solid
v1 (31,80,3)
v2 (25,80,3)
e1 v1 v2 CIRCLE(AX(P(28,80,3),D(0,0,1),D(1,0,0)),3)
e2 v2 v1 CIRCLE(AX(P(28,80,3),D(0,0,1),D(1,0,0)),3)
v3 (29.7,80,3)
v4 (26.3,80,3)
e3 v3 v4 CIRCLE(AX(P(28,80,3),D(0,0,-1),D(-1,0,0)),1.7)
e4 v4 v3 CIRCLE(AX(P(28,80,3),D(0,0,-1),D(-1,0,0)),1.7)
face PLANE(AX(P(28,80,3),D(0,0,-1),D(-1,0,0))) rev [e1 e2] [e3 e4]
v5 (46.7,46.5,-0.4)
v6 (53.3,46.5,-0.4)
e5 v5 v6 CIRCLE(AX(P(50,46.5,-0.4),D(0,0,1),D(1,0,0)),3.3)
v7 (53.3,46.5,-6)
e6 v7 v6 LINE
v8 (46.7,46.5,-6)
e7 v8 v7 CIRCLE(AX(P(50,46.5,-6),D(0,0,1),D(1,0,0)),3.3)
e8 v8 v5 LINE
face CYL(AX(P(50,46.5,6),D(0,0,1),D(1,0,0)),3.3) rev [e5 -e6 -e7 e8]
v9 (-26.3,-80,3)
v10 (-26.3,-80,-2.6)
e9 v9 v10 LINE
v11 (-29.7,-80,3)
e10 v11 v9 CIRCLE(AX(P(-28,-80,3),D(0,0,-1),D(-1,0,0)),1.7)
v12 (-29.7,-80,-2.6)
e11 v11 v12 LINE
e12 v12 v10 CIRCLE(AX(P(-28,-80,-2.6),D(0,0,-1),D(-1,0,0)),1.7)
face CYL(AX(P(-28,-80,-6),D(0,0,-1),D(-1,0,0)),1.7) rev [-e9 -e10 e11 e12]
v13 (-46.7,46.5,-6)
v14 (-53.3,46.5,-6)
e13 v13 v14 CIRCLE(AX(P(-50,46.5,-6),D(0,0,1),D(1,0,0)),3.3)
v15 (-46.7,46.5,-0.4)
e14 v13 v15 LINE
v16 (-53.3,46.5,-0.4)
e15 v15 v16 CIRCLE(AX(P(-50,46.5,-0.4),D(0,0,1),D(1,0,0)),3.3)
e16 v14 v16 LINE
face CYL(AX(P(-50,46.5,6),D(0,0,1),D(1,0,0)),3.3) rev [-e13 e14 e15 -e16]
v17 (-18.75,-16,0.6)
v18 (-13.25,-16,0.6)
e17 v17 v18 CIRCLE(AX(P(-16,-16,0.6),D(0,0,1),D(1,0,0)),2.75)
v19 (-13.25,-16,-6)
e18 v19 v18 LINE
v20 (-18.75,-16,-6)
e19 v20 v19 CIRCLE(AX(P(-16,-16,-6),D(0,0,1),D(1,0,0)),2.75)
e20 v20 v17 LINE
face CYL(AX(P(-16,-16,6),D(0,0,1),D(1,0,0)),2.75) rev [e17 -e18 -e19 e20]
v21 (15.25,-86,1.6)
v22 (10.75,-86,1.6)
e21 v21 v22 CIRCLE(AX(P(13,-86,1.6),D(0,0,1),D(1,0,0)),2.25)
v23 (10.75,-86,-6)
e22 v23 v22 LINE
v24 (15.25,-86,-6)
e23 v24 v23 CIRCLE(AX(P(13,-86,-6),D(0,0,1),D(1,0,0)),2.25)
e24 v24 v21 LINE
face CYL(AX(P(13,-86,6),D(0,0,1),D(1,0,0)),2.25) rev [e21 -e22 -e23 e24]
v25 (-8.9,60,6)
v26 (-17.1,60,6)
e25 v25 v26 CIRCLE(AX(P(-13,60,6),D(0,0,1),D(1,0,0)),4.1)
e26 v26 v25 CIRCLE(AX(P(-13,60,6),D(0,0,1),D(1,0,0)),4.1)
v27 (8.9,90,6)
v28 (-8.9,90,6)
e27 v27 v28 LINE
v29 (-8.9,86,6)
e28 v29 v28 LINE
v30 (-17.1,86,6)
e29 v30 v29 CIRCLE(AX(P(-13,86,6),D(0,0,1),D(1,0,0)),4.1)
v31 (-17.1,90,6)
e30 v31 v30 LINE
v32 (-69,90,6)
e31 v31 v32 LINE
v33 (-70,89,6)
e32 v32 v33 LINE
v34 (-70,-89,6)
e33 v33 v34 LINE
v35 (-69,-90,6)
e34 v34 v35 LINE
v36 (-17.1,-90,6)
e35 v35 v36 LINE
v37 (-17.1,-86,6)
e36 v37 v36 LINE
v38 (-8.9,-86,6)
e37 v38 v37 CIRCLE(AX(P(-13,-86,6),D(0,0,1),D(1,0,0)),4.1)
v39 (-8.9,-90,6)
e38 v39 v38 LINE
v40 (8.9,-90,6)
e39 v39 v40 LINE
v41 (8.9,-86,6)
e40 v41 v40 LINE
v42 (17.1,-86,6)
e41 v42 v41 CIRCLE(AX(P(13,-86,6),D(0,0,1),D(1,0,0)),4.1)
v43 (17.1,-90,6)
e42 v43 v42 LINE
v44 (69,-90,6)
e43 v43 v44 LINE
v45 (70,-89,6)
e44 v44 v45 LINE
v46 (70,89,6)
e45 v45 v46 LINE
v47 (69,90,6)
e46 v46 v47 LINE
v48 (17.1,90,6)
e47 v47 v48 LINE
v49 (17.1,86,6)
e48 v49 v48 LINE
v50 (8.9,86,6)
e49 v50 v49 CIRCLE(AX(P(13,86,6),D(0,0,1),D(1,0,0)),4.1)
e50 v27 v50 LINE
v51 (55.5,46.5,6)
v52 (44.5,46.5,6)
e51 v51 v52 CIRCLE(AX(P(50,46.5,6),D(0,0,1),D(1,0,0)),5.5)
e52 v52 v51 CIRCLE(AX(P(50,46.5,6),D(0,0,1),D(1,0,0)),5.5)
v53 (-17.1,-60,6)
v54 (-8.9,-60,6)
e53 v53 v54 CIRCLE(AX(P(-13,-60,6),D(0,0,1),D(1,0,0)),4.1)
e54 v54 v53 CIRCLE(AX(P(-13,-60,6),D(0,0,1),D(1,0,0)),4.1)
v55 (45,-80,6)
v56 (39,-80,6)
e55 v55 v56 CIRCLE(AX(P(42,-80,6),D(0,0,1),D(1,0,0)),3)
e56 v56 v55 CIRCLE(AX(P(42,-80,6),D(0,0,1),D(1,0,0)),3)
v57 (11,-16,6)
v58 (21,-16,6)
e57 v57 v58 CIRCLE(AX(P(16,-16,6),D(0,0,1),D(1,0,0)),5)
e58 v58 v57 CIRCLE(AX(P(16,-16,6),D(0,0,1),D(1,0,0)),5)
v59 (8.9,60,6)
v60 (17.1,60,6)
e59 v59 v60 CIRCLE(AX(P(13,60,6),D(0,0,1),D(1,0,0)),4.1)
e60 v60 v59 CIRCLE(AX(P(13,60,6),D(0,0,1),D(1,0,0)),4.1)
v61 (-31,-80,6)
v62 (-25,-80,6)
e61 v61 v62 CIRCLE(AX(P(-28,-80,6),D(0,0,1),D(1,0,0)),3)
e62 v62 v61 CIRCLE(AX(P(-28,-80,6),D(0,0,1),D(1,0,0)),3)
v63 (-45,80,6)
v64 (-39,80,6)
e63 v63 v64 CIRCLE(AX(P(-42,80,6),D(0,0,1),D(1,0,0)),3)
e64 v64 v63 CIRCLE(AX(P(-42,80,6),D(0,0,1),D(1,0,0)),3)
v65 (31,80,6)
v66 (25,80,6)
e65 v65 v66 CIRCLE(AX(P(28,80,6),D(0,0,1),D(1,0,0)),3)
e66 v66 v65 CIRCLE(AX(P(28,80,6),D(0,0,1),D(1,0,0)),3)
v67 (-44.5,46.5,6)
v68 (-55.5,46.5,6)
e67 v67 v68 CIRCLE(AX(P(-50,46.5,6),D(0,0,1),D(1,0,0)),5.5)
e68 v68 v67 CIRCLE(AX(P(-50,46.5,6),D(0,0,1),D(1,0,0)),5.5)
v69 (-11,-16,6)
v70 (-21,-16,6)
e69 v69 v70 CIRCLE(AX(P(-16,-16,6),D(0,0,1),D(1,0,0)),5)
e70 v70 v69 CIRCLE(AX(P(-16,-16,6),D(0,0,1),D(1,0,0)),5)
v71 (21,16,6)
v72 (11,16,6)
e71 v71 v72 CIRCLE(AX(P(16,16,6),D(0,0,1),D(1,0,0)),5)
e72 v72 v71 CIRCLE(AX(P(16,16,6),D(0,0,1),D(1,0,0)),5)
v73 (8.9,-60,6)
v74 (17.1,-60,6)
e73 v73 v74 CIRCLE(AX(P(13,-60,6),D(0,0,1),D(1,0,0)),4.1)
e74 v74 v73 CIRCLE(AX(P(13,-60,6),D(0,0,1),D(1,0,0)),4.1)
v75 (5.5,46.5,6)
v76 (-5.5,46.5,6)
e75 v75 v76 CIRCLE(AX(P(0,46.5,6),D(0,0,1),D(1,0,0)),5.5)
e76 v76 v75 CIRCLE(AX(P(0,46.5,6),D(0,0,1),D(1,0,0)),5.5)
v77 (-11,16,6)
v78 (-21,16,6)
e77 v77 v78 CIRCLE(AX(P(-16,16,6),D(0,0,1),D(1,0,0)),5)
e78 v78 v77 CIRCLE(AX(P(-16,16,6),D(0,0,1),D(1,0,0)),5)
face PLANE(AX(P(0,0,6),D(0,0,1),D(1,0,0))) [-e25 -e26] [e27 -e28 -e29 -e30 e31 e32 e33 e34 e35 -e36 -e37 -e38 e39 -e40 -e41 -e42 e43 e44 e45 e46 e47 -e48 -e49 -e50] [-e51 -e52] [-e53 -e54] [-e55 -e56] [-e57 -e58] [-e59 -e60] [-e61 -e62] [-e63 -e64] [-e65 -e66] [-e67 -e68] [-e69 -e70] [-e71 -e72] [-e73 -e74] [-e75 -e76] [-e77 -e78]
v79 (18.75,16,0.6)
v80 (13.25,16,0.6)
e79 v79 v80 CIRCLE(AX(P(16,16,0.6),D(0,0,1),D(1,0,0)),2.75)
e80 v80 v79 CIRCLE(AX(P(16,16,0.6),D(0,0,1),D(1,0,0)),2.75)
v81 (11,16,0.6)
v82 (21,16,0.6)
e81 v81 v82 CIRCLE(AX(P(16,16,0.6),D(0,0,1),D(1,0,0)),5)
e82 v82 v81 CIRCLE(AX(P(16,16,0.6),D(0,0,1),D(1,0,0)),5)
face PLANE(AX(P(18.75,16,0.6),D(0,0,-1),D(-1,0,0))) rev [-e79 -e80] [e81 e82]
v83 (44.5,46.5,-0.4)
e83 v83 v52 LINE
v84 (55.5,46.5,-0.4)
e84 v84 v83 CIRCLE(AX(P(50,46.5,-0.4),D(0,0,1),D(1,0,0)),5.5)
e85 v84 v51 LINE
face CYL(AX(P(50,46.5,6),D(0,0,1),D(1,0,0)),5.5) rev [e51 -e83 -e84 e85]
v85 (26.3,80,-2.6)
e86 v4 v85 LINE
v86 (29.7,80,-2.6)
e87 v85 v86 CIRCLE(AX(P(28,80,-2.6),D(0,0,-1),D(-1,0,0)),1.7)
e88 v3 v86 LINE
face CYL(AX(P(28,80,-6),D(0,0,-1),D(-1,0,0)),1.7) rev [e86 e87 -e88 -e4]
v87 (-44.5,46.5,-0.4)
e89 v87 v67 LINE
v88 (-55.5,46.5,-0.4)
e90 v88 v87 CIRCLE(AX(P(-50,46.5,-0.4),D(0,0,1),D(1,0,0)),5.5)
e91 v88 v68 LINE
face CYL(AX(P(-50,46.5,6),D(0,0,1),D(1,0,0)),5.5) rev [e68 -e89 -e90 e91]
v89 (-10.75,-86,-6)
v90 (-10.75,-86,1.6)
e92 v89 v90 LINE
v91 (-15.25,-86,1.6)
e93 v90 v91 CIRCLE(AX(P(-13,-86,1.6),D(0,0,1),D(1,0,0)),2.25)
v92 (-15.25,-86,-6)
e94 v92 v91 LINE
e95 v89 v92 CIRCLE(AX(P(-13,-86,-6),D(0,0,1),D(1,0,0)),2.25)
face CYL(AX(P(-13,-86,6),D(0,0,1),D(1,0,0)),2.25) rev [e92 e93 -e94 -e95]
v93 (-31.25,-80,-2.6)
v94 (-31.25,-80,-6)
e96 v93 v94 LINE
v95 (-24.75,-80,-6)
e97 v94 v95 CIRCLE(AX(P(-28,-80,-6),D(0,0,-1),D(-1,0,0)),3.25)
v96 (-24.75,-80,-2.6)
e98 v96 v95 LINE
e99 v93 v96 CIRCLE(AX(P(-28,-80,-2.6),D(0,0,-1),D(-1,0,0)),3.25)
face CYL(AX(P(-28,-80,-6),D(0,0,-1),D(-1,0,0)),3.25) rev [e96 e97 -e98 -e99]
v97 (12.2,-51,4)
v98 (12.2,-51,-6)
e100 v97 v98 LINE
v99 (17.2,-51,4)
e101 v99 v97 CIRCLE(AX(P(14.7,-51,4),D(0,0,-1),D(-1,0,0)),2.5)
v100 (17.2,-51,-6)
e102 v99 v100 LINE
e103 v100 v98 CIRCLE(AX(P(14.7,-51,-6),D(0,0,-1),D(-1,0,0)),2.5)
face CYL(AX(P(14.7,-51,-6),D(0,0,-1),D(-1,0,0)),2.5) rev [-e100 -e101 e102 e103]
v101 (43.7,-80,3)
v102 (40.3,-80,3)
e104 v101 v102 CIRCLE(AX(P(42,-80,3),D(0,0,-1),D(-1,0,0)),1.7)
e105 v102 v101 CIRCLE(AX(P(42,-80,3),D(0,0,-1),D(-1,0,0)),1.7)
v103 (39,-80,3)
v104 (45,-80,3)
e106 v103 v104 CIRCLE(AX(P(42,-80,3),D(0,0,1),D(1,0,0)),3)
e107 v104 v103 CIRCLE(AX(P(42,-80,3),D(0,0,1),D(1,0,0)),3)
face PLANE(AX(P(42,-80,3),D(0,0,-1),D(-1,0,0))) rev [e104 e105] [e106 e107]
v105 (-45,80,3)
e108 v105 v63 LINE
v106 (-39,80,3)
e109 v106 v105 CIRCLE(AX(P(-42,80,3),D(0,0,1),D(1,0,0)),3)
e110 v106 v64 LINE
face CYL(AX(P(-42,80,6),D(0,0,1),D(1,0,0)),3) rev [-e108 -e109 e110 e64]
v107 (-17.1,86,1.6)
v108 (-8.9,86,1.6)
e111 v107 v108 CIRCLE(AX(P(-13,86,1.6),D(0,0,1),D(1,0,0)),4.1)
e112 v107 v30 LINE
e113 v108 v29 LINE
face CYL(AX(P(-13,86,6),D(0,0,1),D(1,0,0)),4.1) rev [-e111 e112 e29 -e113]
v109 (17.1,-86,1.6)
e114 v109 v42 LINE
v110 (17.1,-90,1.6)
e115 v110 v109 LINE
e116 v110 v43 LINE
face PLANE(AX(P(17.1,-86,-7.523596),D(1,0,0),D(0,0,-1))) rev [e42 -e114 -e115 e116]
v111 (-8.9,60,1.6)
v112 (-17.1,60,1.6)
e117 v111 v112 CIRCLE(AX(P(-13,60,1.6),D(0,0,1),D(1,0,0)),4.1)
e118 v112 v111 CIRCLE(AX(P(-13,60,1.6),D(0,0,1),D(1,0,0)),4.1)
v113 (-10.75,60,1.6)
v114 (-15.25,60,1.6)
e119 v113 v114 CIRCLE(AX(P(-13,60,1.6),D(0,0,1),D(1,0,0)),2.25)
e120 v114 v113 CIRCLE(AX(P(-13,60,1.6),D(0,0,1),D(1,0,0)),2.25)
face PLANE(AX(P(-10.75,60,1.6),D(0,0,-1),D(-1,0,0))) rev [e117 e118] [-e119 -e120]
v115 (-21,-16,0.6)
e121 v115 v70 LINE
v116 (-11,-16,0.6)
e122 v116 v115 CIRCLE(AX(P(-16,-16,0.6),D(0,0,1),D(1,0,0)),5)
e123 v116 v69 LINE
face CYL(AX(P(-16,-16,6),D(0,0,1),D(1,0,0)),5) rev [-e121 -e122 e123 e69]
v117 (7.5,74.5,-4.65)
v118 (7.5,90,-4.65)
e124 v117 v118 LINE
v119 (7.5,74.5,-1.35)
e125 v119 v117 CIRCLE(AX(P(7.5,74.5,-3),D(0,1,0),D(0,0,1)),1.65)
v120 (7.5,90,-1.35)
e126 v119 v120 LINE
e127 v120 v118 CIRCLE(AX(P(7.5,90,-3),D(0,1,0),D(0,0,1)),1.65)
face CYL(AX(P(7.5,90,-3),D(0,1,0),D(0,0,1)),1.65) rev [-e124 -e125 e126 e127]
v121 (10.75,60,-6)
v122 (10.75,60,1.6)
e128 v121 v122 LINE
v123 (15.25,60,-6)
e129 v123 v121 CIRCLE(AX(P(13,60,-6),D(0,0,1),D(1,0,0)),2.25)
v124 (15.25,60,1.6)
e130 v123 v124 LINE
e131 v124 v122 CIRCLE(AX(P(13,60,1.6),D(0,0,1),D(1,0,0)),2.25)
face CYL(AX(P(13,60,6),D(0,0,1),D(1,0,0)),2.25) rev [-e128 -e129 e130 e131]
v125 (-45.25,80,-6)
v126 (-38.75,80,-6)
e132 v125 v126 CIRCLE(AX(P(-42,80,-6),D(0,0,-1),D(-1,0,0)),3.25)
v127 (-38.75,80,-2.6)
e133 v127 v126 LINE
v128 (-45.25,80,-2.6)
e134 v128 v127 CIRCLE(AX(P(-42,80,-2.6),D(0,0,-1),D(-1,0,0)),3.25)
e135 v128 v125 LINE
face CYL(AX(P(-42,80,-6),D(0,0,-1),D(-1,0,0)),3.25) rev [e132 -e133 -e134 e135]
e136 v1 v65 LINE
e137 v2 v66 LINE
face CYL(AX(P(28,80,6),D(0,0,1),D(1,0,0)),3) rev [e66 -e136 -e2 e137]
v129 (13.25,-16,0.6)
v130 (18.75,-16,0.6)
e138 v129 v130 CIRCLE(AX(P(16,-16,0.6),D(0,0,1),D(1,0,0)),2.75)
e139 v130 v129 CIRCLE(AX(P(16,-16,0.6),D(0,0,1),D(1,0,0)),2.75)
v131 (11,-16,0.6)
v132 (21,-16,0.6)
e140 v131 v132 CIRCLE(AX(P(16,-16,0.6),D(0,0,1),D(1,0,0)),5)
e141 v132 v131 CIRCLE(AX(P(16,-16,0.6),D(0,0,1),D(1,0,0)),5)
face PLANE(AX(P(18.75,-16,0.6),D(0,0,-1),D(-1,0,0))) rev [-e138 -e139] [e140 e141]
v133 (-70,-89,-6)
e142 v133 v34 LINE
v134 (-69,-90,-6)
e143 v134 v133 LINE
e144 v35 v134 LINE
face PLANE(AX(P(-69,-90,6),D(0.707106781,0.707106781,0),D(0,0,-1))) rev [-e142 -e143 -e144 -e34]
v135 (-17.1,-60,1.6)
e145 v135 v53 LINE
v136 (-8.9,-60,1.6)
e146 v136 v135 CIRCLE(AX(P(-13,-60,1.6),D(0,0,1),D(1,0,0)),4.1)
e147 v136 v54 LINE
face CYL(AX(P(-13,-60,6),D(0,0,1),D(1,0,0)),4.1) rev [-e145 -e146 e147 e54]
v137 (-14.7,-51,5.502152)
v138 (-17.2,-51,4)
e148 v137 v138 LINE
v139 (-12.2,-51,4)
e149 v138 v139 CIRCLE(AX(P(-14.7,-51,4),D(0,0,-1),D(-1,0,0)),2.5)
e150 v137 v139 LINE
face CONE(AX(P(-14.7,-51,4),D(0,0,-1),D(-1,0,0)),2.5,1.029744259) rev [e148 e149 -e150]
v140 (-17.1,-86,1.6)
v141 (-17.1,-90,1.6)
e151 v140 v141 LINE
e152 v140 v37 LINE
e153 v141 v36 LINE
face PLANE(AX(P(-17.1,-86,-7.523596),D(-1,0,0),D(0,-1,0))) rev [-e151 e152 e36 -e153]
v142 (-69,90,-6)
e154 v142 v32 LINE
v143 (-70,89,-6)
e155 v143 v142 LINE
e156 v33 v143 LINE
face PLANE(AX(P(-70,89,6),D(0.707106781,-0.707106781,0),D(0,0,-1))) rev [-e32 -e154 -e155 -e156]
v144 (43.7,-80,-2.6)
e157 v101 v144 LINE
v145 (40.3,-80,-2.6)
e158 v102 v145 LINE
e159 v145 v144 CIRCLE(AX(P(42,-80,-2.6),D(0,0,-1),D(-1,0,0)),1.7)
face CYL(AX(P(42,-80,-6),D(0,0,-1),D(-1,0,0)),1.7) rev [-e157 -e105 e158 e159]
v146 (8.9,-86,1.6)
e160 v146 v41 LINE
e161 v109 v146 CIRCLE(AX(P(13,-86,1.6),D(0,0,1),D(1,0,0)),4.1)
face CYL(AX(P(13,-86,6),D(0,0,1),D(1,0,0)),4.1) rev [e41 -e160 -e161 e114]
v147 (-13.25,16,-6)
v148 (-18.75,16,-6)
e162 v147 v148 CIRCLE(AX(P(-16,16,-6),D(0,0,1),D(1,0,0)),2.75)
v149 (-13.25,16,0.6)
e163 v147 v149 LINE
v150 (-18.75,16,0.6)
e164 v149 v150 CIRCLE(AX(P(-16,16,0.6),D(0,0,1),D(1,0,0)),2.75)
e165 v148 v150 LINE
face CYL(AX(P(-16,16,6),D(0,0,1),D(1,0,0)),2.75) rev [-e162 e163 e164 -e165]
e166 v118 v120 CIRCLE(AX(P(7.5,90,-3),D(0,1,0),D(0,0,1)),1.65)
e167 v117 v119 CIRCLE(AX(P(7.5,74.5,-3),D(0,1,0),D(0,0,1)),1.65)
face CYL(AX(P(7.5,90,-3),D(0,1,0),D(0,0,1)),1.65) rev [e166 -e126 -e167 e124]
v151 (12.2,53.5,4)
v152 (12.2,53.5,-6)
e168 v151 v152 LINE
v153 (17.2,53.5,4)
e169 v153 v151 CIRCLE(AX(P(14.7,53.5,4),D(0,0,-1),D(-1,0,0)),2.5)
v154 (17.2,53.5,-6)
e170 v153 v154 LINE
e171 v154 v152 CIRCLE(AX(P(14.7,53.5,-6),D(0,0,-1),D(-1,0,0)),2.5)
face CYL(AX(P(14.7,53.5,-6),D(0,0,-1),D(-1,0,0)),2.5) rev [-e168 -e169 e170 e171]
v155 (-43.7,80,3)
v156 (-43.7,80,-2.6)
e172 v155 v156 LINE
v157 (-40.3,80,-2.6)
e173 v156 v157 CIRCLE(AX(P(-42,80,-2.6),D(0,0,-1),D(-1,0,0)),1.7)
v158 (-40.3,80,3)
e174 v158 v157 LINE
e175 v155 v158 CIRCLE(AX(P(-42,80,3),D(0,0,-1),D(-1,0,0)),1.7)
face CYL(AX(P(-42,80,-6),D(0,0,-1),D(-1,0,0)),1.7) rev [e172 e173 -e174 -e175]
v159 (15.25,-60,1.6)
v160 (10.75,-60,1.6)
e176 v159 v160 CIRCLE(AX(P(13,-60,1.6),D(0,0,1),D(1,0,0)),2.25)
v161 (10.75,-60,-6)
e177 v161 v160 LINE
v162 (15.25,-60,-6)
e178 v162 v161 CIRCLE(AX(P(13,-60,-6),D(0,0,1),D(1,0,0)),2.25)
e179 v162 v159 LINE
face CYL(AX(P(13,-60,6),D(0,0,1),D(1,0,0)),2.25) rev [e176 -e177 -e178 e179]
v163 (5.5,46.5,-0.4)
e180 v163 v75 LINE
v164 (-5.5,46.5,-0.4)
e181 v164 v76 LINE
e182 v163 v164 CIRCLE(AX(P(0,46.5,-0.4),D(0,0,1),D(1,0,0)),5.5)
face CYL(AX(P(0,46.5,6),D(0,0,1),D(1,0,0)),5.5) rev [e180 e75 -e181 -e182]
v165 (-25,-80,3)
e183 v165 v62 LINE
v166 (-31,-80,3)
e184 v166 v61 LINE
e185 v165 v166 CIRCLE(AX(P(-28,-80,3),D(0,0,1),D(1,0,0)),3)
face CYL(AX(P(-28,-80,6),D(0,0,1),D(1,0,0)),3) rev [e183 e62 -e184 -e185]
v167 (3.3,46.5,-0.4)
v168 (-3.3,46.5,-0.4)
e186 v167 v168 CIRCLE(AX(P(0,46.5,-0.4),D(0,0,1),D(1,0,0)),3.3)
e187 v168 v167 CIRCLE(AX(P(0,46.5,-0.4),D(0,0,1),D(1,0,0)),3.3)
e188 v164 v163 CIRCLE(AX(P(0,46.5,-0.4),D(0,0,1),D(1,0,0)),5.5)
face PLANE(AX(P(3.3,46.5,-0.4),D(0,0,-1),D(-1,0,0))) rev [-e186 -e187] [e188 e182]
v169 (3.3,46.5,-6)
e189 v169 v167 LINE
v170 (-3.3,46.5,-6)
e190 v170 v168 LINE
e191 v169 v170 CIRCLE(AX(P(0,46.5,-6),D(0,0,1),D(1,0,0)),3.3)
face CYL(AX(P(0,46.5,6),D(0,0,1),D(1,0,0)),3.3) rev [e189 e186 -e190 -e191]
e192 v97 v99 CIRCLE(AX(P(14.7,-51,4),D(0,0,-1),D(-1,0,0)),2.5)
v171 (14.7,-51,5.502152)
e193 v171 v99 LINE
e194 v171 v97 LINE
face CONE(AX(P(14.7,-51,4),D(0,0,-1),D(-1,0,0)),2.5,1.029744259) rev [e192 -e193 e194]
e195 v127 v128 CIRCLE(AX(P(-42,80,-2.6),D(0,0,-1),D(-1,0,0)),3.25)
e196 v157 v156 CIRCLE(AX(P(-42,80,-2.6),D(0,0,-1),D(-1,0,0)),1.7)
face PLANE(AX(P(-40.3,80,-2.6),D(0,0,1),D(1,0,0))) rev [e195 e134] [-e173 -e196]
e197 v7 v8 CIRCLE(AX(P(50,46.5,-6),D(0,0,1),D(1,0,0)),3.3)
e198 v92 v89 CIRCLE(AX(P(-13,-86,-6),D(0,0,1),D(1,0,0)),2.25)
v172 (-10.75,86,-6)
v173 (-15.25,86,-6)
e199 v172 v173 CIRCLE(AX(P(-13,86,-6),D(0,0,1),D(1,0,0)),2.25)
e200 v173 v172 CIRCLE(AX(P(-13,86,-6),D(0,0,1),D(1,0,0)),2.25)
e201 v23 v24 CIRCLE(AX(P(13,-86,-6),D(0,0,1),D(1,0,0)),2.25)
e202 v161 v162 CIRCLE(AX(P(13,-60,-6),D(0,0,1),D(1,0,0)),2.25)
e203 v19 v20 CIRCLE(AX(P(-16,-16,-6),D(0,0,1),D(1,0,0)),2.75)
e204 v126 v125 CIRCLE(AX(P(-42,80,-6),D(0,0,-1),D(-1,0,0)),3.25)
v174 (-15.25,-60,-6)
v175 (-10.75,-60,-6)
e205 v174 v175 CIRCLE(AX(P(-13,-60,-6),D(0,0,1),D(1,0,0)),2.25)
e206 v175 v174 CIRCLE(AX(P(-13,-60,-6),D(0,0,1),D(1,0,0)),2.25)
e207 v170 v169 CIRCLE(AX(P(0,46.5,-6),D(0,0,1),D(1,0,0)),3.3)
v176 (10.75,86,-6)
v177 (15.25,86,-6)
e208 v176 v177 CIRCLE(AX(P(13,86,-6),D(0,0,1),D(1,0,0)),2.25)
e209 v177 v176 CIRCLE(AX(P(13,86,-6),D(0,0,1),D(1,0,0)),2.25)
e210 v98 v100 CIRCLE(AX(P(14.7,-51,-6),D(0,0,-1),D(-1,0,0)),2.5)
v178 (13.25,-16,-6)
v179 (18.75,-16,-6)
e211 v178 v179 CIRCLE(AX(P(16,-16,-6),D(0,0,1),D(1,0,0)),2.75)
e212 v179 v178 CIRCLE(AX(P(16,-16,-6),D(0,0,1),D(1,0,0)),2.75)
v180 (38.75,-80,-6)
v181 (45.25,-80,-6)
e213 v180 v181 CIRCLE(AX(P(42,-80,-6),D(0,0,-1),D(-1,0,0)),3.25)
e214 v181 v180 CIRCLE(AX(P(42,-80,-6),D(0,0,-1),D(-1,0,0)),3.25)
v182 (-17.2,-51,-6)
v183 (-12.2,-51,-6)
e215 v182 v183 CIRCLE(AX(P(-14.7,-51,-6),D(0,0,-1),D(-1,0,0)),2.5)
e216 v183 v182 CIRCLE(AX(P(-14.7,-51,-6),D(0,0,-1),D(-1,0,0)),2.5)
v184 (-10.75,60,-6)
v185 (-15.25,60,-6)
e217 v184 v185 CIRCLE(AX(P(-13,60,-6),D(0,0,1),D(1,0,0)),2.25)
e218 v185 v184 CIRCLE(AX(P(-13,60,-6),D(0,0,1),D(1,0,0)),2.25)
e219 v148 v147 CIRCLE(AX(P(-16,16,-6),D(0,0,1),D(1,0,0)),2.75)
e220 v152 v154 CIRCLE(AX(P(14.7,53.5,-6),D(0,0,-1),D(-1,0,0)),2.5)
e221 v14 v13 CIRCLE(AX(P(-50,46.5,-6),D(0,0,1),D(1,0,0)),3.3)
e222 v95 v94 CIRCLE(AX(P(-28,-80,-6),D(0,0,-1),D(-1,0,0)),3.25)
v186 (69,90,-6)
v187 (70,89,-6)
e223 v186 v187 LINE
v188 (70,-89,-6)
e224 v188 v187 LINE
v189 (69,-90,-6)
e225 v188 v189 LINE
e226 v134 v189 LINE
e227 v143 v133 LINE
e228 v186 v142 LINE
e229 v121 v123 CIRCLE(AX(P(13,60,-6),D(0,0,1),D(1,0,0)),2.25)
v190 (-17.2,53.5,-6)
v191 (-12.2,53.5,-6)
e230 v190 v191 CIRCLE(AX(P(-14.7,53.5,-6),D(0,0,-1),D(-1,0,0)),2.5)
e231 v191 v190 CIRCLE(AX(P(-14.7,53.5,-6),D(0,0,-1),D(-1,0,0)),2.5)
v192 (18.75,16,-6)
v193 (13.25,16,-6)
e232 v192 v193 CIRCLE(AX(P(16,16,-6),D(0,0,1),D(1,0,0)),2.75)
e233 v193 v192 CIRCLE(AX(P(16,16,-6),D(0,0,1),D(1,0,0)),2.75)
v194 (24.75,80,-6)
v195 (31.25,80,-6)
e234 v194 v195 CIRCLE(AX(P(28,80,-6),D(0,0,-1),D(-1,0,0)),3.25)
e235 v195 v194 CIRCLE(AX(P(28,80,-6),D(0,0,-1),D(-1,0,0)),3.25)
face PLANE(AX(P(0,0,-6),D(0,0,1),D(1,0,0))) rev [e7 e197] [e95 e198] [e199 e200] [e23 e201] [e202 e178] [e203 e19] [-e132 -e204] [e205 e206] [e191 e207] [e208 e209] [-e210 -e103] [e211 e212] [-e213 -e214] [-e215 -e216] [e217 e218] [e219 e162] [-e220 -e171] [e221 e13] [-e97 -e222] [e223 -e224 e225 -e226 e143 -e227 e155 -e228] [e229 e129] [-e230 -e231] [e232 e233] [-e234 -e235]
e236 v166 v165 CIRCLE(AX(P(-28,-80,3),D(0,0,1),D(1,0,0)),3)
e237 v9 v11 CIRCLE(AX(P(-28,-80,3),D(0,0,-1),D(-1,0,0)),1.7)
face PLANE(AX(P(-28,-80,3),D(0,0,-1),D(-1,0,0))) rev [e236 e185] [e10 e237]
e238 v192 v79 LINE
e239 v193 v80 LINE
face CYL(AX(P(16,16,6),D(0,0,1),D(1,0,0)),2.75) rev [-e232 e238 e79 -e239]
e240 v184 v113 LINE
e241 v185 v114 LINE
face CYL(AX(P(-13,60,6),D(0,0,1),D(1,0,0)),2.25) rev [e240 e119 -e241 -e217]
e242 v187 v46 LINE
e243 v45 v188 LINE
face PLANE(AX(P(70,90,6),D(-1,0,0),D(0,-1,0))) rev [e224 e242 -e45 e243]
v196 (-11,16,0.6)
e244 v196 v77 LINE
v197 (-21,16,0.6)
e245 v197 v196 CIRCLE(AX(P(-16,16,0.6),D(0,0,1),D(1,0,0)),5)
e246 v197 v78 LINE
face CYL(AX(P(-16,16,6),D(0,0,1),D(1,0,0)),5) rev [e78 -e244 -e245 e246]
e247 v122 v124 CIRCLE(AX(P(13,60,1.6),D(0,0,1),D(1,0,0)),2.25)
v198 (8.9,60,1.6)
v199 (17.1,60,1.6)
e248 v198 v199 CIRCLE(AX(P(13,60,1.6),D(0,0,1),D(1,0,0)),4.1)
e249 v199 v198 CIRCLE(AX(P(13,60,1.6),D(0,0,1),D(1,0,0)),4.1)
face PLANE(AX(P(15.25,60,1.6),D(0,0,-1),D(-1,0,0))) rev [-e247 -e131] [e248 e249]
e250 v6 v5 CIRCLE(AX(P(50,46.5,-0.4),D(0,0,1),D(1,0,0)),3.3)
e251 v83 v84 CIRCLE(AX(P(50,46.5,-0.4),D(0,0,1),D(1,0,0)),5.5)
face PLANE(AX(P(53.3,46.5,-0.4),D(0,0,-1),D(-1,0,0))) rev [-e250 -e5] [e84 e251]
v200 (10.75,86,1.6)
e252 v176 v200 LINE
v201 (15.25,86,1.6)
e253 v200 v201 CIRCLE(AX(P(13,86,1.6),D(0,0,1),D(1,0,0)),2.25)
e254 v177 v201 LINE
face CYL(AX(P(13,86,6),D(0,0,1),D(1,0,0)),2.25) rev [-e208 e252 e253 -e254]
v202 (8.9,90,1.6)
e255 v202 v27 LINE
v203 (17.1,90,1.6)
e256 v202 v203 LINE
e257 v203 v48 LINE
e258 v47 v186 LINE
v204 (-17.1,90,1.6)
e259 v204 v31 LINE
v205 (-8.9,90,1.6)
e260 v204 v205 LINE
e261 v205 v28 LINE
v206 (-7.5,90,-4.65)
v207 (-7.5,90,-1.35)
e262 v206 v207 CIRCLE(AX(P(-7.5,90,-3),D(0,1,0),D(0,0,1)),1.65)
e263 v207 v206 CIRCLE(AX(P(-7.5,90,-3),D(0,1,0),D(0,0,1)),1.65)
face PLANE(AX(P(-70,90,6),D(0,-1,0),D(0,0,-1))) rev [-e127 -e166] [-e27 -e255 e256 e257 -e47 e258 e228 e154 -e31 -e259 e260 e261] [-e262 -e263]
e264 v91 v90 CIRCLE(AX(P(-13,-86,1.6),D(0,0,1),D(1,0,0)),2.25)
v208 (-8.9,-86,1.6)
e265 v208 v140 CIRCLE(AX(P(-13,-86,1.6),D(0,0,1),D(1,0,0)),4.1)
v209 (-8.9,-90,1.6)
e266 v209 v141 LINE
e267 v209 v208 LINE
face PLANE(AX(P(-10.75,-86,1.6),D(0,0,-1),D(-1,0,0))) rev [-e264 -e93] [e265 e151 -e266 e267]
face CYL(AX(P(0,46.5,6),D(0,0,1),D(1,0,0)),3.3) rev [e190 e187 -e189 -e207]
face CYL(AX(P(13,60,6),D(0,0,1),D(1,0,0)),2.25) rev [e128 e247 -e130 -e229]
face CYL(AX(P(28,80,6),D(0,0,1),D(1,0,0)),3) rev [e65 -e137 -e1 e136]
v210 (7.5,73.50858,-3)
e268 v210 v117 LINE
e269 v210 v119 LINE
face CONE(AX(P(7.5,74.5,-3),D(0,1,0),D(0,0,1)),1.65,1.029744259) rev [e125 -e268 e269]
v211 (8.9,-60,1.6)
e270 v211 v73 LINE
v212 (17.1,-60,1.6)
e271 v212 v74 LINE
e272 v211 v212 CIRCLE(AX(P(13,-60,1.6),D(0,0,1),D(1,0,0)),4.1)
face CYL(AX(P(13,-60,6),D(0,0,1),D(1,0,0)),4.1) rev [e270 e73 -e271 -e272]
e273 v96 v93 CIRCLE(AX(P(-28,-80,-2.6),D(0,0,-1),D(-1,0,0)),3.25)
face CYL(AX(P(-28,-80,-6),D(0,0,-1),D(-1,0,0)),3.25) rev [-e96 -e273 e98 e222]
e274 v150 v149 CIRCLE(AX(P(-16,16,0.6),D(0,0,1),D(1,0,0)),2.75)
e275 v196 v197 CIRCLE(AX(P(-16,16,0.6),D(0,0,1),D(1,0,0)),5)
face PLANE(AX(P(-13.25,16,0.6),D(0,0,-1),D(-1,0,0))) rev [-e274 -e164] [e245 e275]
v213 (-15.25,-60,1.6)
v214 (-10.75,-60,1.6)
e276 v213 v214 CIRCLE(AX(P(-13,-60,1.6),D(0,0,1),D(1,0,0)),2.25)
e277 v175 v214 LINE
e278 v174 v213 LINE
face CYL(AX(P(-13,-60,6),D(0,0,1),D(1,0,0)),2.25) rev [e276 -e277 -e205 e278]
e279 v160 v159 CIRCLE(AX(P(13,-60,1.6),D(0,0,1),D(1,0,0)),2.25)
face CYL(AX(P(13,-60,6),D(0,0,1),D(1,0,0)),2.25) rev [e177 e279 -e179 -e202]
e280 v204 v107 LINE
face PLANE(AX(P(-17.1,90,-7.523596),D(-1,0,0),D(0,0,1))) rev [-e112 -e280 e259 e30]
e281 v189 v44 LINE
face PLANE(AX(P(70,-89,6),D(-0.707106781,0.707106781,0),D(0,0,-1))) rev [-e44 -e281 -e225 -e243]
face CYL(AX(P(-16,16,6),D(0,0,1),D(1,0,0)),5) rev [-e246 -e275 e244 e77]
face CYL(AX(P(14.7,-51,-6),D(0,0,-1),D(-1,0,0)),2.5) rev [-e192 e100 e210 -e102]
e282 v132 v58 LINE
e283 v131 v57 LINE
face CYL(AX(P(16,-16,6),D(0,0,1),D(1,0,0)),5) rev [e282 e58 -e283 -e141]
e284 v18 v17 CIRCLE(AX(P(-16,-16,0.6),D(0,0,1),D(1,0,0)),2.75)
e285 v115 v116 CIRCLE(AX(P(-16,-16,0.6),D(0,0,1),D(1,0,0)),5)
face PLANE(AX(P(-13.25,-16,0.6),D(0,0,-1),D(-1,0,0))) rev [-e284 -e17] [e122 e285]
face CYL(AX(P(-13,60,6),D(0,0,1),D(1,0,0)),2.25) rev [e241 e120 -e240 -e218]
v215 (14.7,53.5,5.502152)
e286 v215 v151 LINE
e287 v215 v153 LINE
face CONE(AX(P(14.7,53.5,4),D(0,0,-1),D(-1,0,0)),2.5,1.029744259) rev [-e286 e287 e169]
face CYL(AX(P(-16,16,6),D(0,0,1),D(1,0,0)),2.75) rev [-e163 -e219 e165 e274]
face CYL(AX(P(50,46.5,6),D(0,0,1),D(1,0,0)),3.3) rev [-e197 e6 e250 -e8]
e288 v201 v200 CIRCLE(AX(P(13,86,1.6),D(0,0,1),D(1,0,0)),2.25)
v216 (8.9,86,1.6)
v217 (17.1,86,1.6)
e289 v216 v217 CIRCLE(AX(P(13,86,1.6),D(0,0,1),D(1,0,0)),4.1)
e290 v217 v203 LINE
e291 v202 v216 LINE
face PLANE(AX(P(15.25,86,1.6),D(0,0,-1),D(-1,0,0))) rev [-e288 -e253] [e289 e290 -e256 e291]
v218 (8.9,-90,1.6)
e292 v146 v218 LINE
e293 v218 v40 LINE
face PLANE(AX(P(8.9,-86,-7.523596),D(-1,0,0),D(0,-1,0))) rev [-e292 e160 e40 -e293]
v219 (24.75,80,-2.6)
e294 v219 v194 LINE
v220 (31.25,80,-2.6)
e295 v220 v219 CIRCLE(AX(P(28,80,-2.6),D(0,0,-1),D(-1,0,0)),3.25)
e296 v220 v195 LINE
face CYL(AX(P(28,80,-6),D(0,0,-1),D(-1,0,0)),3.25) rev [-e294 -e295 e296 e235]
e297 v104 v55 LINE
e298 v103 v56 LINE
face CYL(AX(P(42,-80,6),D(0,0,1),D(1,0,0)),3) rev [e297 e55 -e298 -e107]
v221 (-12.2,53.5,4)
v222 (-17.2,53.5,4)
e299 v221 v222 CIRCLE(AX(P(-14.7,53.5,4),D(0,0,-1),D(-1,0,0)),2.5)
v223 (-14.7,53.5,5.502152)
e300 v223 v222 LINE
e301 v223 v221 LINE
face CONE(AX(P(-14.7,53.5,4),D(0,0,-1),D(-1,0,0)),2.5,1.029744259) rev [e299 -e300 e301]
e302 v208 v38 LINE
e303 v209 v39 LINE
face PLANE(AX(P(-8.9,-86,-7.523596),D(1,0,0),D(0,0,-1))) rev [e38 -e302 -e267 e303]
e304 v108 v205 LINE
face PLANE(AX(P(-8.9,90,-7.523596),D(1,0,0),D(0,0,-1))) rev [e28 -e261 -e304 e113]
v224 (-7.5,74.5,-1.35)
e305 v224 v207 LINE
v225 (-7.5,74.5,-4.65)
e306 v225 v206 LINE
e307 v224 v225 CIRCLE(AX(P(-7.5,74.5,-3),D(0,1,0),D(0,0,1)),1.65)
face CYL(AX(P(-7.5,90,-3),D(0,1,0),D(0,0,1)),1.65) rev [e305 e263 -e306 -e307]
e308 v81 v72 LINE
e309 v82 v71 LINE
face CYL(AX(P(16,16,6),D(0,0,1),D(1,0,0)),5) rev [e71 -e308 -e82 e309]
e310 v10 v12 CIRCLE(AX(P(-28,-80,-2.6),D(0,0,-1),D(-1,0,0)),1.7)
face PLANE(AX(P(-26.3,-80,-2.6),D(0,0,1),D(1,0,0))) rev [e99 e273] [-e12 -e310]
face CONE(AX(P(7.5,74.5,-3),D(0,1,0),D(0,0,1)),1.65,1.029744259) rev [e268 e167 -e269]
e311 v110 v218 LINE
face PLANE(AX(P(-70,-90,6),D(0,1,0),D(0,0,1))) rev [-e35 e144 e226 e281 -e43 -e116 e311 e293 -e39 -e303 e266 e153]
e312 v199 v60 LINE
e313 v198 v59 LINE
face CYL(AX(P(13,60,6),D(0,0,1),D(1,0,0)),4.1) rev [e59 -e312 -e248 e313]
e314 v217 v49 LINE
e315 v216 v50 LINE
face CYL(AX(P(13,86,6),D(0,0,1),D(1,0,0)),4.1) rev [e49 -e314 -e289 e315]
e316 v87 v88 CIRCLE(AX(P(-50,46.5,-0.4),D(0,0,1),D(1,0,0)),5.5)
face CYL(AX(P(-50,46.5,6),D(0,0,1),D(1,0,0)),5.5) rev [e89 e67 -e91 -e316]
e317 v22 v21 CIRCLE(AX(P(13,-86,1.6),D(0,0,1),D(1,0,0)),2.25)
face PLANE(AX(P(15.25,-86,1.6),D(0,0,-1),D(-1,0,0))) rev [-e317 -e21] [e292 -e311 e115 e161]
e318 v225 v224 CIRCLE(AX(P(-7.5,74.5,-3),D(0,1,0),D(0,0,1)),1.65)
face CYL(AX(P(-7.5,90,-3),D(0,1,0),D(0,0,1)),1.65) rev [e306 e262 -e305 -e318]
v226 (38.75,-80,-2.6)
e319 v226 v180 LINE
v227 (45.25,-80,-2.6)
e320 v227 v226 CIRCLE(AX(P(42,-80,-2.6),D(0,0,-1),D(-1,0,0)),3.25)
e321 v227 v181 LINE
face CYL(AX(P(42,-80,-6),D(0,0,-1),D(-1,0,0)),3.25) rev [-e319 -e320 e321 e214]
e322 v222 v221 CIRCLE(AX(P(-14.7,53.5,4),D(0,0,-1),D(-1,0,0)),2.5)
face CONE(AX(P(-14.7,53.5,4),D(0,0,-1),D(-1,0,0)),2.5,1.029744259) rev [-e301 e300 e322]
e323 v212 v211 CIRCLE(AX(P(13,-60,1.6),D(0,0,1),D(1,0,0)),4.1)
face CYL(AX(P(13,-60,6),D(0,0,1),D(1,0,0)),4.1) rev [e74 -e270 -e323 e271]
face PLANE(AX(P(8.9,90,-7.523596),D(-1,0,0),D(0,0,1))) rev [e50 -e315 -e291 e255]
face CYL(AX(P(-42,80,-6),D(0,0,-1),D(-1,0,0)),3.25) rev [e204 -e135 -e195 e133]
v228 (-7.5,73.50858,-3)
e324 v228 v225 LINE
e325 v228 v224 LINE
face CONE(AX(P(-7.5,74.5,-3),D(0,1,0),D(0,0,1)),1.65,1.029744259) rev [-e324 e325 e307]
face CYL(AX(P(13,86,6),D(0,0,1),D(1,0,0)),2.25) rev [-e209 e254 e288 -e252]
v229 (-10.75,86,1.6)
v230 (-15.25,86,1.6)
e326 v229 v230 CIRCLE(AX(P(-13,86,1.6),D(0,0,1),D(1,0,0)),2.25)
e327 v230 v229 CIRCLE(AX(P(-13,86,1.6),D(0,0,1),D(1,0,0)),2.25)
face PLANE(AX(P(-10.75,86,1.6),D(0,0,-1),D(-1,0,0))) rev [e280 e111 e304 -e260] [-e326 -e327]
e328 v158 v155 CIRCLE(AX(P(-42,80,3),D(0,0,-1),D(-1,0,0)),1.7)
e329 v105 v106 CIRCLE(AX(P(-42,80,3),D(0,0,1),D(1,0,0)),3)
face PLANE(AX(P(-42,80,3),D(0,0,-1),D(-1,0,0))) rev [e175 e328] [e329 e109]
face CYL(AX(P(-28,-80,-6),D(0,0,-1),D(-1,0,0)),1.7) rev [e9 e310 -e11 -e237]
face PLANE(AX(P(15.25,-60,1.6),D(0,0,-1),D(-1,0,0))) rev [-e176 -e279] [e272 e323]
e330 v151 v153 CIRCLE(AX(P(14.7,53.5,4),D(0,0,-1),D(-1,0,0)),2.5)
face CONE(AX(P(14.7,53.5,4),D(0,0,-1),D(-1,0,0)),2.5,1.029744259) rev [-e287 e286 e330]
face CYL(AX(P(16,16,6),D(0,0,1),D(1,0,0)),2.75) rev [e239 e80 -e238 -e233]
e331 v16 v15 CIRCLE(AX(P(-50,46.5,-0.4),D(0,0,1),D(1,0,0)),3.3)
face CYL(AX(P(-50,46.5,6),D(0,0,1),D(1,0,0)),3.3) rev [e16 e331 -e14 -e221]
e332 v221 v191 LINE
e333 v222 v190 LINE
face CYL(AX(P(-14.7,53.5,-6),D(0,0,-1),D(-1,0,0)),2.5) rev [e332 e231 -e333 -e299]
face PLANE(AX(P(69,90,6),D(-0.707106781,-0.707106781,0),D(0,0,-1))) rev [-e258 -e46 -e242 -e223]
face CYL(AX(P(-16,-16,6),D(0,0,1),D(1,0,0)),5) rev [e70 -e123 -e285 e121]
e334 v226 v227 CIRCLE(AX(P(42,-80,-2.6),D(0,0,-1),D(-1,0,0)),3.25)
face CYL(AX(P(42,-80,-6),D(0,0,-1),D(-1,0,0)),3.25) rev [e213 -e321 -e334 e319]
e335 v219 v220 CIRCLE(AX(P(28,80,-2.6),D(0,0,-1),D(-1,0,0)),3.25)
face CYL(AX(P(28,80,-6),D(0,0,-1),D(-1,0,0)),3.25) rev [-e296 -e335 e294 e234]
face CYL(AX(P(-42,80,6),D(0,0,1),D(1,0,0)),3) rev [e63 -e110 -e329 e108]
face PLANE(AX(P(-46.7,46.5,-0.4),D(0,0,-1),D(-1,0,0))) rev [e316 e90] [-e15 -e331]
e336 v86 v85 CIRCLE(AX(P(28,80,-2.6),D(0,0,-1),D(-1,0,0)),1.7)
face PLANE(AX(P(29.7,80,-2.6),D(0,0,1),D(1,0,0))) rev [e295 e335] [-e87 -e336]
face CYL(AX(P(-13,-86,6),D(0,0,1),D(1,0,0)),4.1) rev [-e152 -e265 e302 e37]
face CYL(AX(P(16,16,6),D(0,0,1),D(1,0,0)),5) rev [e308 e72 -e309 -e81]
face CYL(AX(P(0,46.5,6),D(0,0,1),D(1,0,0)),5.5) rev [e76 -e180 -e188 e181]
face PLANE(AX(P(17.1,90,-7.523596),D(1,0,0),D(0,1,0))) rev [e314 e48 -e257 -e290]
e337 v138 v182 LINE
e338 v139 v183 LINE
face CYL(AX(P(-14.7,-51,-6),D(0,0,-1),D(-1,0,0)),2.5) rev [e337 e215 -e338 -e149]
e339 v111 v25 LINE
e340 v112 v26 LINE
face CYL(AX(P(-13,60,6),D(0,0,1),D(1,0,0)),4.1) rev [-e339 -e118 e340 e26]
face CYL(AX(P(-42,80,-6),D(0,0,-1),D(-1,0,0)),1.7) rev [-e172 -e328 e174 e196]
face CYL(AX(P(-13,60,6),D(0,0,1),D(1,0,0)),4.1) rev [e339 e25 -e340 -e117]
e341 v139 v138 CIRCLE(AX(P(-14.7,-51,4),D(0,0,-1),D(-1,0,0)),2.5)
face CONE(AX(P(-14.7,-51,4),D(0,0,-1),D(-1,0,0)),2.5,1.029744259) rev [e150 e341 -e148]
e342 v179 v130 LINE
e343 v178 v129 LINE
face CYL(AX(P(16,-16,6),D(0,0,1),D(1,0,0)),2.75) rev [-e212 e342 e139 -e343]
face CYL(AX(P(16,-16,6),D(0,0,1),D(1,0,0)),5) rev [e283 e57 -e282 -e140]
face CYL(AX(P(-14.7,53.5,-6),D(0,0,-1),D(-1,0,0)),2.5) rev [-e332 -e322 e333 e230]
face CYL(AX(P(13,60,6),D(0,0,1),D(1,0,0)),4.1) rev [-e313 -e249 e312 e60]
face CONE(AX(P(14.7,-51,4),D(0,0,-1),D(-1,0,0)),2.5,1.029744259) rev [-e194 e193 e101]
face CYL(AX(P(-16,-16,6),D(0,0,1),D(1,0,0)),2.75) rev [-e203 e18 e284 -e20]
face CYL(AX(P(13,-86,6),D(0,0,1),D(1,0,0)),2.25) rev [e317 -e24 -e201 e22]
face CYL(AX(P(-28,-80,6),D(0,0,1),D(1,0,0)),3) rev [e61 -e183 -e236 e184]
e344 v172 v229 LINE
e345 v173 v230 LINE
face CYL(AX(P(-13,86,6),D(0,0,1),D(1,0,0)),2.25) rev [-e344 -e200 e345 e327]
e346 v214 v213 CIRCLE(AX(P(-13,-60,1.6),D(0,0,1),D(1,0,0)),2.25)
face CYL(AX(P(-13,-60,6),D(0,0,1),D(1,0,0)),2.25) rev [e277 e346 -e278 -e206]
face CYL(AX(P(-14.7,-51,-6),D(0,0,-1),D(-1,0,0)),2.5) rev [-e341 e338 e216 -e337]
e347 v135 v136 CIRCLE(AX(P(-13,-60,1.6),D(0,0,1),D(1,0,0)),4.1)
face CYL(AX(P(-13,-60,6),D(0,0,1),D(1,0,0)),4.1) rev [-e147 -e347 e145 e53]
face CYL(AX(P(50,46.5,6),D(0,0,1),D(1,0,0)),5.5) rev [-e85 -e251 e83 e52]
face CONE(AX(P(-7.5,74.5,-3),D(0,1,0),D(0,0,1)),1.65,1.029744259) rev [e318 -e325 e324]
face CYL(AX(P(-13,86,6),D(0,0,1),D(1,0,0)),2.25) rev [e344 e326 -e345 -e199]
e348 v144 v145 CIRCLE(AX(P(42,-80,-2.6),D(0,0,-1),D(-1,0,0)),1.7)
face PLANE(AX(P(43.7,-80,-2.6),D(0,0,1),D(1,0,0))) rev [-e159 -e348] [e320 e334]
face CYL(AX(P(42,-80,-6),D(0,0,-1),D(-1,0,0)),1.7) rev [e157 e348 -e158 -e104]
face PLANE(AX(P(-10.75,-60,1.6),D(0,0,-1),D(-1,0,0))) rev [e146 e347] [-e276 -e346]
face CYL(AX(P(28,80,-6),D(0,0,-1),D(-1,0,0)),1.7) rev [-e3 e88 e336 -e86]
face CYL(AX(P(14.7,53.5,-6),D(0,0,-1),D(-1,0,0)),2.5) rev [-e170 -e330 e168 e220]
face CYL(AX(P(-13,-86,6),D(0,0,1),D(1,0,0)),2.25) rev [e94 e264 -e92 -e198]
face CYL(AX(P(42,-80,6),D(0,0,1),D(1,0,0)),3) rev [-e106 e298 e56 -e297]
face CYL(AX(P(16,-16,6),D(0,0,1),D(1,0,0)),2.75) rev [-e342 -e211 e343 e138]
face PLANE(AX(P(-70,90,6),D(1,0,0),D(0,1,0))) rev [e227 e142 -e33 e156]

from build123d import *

# Parameters (mm, degrees)
SKETCH1_W                                           = 140
SKETCH1_H                                           = 180
BOSS_EXTRUDE1_DEPTH                                 = 6
CBORE_FOR_M4_HEX_SOCKET_HEAD_CAP_SCREW2_D           = 4.5
CBORE_FOR_M4_HEX_SOCKET_HEAD_CAP_SCREW2_CBORE_D     = 8.2
CBORE_FOR_M4_HEX_SOCKET_HEAD_CAP_SCREW2_CBORE_DEPTH = 4.4
SIZE_MM_DOWEL_HOLE_1_D                              = 5
SIZE_MM_DOWEL_HOLE_1_DEPTH                          = 10
SIZE_MM_DOWEL_HOLE_1_TIP                            = 1.502151548
CBORE_FOR_M5_HEX_SOCKET_HEAD_CAP_SCREW1_D           = 5.5
CBORE_FOR_M5_HEX_SOCKET_HEAD_CAP_SCREW1_CBORE_D     = 10
CBORE_FOR_M5_HEX_SOCKET_HEAD_CAP_SCREW1_CBORE_DEPTH = 5.4
SKETCH10_W                                          = 8.2
SKETCH10_H                                          = 4
CUT_EXTRUDE1_DEPTH                                  = 4.4
M4_TAPPED_HOLE1_D                                   = 3.3
M4_TAPPED_HOLE1_DEPTH                               = 15.5
M4_TAPPED_HOLE1_TIP                                 = 0.991420021
SIZE_MM_DOWEL_HOLE_2_D                              = 6
SIZE_MM_DOWEL_HOLE_2_DEPTH                          = 3
CBORE_FOR_M3_HEX_SOCKET_HEAD_CAP_SCREW1_D           = 3.4
CBORE_FOR_M3_HEX_SOCKET_HEAD_CAP_SCREW1_CBORE_D     = 6.5
CBORE_FOR_M3_HEX_SOCKET_HEAD_CAP_SCREW1_CBORE_DEPTH = 3.4
CHAMFER1_SIZE                                       = 1
CBORE_FOR_M6_HEX_SOCKET_HEAD_CAP_SCREW1_D           = 6.6
CBORE_FOR_M6_HEX_SOCKET_HEAD_CAP_SCREW1_CBORE_D     = 11
CBORE_FOR_M6_HEX_SOCKET_HEAD_CAP_SCREW1_CBORE_DEPTH = 6.4


with BuildPart() as part:
    # Sketch1 → Boss-Extrude1 (new, symmetric)
    with BuildSketch(Plane.XY):
        Rectangle(SKETCH1_W, SKETCH1_H)
    extrude(amount=BOSS_EXTRUDE1_DEPTH, both=True)

    # CBORE for M4 Hex Socket Head Cap Screw2 (through all)
    with Locations(Plane.XY.offset(6)):
        with Locations((13, -60), (-13, -60), (-13, -86), (13, -86), (-13, 86), (13, 86), (-13, 60), (13, 60)):
            CounterBoreHole(CBORE_FOR_M4_HEX_SOCKET_HEAD_CAP_SCREW2_D / 2, CBORE_FOR_M4_HEX_SOCKET_HEAD_CAP_SCREW2_CBORE_D / 2, CBORE_FOR_M4_HEX_SOCKET_HEAD_CAP_SCREW2_CBORE_DEPTH)

    # Size mm dowel hole 1
    with Locations(Plane(origin=(0, 0, -6), x_dir=(-1, 0, 0), z_dir=(0, 0, -1))):
        with Locations((14.7, -51), (-14.7, -51), (14.7, 53.5), (-14.7, 53.5)):
            Hole(SIZE_MM_DOWEL_HOLE_1_D / 2, depth=SIZE_MM_DOWEL_HOLE_1_DEPTH)
            with Locations((0, 0, -(SIZE_MM_DOWEL_HOLE_1_DEPTH + SIZE_MM_DOWEL_HOLE_1_TIP / 2))):  # 118° drill point
                Cone(0, SIZE_MM_DOWEL_HOLE_1_D / 2, SIZE_MM_DOWEL_HOLE_1_TIP, mode=Mode.SUBTRACT)

    # CBORE for M5 Hex Socket Head Cap Screw1 (through all)
    with Locations(Plane.XY.offset(6)):
        with Locations((16, 16), (-16, 16), (-16, -16), (16, -16)):
            CounterBoreHole(CBORE_FOR_M5_HEX_SOCKET_HEAD_CAP_SCREW1_D / 2, CBORE_FOR_M5_HEX_SOCKET_HEAD_CAP_SCREW1_CBORE_D / 2, CBORE_FOR_M5_HEX_SOCKET_HEAD_CAP_SCREW1_CBORE_DEPTH)

    # Sketch10 → Cut-Extrude1 (cut)
    with BuildSketch(Plane.XY.offset(6)):
        with Locations((-13, 88)):
            Rectangle(SKETCH10_W, SKETCH10_H)
        with Locations((13, 88)):
            Rectangle(SKETCH10_W, SKETCH10_H)
        with Locations((-13, -88)):
            Rectangle(SKETCH10_W, SKETCH10_H)
        with Locations((13, -88)):
            Rectangle(SKETCH10_W, SKETCH10_H)
    extrude(amount=-CUT_EXTRUDE1_DEPTH, mode=Mode.SUBTRACT)

    # M4 Tapped Hole1
    with Locations(Plane(origin=(0, 90, 0), x_dir=(1, 0, 0), z_dir=(0, 1, 0))):
        with Locations((-7.5, 3), (7.5, 3)):
            Hole(M4_TAPPED_HOLE1_D / 2, depth=M4_TAPPED_HOLE1_DEPTH)
            with Locations((0, 0, -(M4_TAPPED_HOLE1_DEPTH + M4_TAPPED_HOLE1_TIP / 2))):  # 118° drill point
                Cone(0, M4_TAPPED_HOLE1_D / 2, M4_TAPPED_HOLE1_TIP, mode=Mode.SUBTRACT)

    # Size mm dowel hole 2
    with Locations(Plane.XY.offset(6)):
        with Locations((28, 80), (-42, 80), (42, -80), (-28, -80)):
            Hole(SIZE_MM_DOWEL_HOLE_2_D / 2, depth=SIZE_MM_DOWEL_HOLE_2_DEPTH)

    # CBORE for M3 Hex Socket Head Cap Screw1 (through all)
    with Locations(Plane(origin=(0, 0, -6), x_dir=(-1, 0, 0), z_dir=(0, 0, -1))):
        with Locations((-28, 80), (42, 80), (28, -80), (-42, -80)):
            CounterBoreHole(CBORE_FOR_M3_HEX_SOCKET_HEAD_CAP_SCREW1_D / 2, CBORE_FOR_M3_HEX_SOCKET_HEAD_CAP_SCREW1_CBORE_D / 2, CBORE_FOR_M3_HEX_SOCKET_HEAD_CAP_SCREW1_CBORE_DEPTH)

    # Chamfer1
    chamfer1_edges = [part.edges().sort_by_distance(p)[0] for p in [
        (70, -90, 0),
        (-70, -90, 0),
        (-70, 90, 0),
        (70, 90, 0),
    ]]
    chamfer(chamfer1_edges, length=CHAMFER1_SIZE)

    # CBORE for M6 Hex Socket Head Cap Screw1 (through all)
    with Locations(Plane.XY.offset(6)):
        with Locations((-50, 46.5), (0, 46.5), (50, 46.5)):
            CounterBoreHole(CBORE_FOR_M6_HEX_SOCKET_HEAD_CAP_SCREW1_D / 2, CBORE_FOR_M6_HEX_SOCKET_HEAD_CAP_SCREW1_CBORE_D / 2, CBORE_FOR_M6_HEX_SOCKET_HEAD_CAP_SCREW1_CBORE_DEPTH)


solid = part.part
